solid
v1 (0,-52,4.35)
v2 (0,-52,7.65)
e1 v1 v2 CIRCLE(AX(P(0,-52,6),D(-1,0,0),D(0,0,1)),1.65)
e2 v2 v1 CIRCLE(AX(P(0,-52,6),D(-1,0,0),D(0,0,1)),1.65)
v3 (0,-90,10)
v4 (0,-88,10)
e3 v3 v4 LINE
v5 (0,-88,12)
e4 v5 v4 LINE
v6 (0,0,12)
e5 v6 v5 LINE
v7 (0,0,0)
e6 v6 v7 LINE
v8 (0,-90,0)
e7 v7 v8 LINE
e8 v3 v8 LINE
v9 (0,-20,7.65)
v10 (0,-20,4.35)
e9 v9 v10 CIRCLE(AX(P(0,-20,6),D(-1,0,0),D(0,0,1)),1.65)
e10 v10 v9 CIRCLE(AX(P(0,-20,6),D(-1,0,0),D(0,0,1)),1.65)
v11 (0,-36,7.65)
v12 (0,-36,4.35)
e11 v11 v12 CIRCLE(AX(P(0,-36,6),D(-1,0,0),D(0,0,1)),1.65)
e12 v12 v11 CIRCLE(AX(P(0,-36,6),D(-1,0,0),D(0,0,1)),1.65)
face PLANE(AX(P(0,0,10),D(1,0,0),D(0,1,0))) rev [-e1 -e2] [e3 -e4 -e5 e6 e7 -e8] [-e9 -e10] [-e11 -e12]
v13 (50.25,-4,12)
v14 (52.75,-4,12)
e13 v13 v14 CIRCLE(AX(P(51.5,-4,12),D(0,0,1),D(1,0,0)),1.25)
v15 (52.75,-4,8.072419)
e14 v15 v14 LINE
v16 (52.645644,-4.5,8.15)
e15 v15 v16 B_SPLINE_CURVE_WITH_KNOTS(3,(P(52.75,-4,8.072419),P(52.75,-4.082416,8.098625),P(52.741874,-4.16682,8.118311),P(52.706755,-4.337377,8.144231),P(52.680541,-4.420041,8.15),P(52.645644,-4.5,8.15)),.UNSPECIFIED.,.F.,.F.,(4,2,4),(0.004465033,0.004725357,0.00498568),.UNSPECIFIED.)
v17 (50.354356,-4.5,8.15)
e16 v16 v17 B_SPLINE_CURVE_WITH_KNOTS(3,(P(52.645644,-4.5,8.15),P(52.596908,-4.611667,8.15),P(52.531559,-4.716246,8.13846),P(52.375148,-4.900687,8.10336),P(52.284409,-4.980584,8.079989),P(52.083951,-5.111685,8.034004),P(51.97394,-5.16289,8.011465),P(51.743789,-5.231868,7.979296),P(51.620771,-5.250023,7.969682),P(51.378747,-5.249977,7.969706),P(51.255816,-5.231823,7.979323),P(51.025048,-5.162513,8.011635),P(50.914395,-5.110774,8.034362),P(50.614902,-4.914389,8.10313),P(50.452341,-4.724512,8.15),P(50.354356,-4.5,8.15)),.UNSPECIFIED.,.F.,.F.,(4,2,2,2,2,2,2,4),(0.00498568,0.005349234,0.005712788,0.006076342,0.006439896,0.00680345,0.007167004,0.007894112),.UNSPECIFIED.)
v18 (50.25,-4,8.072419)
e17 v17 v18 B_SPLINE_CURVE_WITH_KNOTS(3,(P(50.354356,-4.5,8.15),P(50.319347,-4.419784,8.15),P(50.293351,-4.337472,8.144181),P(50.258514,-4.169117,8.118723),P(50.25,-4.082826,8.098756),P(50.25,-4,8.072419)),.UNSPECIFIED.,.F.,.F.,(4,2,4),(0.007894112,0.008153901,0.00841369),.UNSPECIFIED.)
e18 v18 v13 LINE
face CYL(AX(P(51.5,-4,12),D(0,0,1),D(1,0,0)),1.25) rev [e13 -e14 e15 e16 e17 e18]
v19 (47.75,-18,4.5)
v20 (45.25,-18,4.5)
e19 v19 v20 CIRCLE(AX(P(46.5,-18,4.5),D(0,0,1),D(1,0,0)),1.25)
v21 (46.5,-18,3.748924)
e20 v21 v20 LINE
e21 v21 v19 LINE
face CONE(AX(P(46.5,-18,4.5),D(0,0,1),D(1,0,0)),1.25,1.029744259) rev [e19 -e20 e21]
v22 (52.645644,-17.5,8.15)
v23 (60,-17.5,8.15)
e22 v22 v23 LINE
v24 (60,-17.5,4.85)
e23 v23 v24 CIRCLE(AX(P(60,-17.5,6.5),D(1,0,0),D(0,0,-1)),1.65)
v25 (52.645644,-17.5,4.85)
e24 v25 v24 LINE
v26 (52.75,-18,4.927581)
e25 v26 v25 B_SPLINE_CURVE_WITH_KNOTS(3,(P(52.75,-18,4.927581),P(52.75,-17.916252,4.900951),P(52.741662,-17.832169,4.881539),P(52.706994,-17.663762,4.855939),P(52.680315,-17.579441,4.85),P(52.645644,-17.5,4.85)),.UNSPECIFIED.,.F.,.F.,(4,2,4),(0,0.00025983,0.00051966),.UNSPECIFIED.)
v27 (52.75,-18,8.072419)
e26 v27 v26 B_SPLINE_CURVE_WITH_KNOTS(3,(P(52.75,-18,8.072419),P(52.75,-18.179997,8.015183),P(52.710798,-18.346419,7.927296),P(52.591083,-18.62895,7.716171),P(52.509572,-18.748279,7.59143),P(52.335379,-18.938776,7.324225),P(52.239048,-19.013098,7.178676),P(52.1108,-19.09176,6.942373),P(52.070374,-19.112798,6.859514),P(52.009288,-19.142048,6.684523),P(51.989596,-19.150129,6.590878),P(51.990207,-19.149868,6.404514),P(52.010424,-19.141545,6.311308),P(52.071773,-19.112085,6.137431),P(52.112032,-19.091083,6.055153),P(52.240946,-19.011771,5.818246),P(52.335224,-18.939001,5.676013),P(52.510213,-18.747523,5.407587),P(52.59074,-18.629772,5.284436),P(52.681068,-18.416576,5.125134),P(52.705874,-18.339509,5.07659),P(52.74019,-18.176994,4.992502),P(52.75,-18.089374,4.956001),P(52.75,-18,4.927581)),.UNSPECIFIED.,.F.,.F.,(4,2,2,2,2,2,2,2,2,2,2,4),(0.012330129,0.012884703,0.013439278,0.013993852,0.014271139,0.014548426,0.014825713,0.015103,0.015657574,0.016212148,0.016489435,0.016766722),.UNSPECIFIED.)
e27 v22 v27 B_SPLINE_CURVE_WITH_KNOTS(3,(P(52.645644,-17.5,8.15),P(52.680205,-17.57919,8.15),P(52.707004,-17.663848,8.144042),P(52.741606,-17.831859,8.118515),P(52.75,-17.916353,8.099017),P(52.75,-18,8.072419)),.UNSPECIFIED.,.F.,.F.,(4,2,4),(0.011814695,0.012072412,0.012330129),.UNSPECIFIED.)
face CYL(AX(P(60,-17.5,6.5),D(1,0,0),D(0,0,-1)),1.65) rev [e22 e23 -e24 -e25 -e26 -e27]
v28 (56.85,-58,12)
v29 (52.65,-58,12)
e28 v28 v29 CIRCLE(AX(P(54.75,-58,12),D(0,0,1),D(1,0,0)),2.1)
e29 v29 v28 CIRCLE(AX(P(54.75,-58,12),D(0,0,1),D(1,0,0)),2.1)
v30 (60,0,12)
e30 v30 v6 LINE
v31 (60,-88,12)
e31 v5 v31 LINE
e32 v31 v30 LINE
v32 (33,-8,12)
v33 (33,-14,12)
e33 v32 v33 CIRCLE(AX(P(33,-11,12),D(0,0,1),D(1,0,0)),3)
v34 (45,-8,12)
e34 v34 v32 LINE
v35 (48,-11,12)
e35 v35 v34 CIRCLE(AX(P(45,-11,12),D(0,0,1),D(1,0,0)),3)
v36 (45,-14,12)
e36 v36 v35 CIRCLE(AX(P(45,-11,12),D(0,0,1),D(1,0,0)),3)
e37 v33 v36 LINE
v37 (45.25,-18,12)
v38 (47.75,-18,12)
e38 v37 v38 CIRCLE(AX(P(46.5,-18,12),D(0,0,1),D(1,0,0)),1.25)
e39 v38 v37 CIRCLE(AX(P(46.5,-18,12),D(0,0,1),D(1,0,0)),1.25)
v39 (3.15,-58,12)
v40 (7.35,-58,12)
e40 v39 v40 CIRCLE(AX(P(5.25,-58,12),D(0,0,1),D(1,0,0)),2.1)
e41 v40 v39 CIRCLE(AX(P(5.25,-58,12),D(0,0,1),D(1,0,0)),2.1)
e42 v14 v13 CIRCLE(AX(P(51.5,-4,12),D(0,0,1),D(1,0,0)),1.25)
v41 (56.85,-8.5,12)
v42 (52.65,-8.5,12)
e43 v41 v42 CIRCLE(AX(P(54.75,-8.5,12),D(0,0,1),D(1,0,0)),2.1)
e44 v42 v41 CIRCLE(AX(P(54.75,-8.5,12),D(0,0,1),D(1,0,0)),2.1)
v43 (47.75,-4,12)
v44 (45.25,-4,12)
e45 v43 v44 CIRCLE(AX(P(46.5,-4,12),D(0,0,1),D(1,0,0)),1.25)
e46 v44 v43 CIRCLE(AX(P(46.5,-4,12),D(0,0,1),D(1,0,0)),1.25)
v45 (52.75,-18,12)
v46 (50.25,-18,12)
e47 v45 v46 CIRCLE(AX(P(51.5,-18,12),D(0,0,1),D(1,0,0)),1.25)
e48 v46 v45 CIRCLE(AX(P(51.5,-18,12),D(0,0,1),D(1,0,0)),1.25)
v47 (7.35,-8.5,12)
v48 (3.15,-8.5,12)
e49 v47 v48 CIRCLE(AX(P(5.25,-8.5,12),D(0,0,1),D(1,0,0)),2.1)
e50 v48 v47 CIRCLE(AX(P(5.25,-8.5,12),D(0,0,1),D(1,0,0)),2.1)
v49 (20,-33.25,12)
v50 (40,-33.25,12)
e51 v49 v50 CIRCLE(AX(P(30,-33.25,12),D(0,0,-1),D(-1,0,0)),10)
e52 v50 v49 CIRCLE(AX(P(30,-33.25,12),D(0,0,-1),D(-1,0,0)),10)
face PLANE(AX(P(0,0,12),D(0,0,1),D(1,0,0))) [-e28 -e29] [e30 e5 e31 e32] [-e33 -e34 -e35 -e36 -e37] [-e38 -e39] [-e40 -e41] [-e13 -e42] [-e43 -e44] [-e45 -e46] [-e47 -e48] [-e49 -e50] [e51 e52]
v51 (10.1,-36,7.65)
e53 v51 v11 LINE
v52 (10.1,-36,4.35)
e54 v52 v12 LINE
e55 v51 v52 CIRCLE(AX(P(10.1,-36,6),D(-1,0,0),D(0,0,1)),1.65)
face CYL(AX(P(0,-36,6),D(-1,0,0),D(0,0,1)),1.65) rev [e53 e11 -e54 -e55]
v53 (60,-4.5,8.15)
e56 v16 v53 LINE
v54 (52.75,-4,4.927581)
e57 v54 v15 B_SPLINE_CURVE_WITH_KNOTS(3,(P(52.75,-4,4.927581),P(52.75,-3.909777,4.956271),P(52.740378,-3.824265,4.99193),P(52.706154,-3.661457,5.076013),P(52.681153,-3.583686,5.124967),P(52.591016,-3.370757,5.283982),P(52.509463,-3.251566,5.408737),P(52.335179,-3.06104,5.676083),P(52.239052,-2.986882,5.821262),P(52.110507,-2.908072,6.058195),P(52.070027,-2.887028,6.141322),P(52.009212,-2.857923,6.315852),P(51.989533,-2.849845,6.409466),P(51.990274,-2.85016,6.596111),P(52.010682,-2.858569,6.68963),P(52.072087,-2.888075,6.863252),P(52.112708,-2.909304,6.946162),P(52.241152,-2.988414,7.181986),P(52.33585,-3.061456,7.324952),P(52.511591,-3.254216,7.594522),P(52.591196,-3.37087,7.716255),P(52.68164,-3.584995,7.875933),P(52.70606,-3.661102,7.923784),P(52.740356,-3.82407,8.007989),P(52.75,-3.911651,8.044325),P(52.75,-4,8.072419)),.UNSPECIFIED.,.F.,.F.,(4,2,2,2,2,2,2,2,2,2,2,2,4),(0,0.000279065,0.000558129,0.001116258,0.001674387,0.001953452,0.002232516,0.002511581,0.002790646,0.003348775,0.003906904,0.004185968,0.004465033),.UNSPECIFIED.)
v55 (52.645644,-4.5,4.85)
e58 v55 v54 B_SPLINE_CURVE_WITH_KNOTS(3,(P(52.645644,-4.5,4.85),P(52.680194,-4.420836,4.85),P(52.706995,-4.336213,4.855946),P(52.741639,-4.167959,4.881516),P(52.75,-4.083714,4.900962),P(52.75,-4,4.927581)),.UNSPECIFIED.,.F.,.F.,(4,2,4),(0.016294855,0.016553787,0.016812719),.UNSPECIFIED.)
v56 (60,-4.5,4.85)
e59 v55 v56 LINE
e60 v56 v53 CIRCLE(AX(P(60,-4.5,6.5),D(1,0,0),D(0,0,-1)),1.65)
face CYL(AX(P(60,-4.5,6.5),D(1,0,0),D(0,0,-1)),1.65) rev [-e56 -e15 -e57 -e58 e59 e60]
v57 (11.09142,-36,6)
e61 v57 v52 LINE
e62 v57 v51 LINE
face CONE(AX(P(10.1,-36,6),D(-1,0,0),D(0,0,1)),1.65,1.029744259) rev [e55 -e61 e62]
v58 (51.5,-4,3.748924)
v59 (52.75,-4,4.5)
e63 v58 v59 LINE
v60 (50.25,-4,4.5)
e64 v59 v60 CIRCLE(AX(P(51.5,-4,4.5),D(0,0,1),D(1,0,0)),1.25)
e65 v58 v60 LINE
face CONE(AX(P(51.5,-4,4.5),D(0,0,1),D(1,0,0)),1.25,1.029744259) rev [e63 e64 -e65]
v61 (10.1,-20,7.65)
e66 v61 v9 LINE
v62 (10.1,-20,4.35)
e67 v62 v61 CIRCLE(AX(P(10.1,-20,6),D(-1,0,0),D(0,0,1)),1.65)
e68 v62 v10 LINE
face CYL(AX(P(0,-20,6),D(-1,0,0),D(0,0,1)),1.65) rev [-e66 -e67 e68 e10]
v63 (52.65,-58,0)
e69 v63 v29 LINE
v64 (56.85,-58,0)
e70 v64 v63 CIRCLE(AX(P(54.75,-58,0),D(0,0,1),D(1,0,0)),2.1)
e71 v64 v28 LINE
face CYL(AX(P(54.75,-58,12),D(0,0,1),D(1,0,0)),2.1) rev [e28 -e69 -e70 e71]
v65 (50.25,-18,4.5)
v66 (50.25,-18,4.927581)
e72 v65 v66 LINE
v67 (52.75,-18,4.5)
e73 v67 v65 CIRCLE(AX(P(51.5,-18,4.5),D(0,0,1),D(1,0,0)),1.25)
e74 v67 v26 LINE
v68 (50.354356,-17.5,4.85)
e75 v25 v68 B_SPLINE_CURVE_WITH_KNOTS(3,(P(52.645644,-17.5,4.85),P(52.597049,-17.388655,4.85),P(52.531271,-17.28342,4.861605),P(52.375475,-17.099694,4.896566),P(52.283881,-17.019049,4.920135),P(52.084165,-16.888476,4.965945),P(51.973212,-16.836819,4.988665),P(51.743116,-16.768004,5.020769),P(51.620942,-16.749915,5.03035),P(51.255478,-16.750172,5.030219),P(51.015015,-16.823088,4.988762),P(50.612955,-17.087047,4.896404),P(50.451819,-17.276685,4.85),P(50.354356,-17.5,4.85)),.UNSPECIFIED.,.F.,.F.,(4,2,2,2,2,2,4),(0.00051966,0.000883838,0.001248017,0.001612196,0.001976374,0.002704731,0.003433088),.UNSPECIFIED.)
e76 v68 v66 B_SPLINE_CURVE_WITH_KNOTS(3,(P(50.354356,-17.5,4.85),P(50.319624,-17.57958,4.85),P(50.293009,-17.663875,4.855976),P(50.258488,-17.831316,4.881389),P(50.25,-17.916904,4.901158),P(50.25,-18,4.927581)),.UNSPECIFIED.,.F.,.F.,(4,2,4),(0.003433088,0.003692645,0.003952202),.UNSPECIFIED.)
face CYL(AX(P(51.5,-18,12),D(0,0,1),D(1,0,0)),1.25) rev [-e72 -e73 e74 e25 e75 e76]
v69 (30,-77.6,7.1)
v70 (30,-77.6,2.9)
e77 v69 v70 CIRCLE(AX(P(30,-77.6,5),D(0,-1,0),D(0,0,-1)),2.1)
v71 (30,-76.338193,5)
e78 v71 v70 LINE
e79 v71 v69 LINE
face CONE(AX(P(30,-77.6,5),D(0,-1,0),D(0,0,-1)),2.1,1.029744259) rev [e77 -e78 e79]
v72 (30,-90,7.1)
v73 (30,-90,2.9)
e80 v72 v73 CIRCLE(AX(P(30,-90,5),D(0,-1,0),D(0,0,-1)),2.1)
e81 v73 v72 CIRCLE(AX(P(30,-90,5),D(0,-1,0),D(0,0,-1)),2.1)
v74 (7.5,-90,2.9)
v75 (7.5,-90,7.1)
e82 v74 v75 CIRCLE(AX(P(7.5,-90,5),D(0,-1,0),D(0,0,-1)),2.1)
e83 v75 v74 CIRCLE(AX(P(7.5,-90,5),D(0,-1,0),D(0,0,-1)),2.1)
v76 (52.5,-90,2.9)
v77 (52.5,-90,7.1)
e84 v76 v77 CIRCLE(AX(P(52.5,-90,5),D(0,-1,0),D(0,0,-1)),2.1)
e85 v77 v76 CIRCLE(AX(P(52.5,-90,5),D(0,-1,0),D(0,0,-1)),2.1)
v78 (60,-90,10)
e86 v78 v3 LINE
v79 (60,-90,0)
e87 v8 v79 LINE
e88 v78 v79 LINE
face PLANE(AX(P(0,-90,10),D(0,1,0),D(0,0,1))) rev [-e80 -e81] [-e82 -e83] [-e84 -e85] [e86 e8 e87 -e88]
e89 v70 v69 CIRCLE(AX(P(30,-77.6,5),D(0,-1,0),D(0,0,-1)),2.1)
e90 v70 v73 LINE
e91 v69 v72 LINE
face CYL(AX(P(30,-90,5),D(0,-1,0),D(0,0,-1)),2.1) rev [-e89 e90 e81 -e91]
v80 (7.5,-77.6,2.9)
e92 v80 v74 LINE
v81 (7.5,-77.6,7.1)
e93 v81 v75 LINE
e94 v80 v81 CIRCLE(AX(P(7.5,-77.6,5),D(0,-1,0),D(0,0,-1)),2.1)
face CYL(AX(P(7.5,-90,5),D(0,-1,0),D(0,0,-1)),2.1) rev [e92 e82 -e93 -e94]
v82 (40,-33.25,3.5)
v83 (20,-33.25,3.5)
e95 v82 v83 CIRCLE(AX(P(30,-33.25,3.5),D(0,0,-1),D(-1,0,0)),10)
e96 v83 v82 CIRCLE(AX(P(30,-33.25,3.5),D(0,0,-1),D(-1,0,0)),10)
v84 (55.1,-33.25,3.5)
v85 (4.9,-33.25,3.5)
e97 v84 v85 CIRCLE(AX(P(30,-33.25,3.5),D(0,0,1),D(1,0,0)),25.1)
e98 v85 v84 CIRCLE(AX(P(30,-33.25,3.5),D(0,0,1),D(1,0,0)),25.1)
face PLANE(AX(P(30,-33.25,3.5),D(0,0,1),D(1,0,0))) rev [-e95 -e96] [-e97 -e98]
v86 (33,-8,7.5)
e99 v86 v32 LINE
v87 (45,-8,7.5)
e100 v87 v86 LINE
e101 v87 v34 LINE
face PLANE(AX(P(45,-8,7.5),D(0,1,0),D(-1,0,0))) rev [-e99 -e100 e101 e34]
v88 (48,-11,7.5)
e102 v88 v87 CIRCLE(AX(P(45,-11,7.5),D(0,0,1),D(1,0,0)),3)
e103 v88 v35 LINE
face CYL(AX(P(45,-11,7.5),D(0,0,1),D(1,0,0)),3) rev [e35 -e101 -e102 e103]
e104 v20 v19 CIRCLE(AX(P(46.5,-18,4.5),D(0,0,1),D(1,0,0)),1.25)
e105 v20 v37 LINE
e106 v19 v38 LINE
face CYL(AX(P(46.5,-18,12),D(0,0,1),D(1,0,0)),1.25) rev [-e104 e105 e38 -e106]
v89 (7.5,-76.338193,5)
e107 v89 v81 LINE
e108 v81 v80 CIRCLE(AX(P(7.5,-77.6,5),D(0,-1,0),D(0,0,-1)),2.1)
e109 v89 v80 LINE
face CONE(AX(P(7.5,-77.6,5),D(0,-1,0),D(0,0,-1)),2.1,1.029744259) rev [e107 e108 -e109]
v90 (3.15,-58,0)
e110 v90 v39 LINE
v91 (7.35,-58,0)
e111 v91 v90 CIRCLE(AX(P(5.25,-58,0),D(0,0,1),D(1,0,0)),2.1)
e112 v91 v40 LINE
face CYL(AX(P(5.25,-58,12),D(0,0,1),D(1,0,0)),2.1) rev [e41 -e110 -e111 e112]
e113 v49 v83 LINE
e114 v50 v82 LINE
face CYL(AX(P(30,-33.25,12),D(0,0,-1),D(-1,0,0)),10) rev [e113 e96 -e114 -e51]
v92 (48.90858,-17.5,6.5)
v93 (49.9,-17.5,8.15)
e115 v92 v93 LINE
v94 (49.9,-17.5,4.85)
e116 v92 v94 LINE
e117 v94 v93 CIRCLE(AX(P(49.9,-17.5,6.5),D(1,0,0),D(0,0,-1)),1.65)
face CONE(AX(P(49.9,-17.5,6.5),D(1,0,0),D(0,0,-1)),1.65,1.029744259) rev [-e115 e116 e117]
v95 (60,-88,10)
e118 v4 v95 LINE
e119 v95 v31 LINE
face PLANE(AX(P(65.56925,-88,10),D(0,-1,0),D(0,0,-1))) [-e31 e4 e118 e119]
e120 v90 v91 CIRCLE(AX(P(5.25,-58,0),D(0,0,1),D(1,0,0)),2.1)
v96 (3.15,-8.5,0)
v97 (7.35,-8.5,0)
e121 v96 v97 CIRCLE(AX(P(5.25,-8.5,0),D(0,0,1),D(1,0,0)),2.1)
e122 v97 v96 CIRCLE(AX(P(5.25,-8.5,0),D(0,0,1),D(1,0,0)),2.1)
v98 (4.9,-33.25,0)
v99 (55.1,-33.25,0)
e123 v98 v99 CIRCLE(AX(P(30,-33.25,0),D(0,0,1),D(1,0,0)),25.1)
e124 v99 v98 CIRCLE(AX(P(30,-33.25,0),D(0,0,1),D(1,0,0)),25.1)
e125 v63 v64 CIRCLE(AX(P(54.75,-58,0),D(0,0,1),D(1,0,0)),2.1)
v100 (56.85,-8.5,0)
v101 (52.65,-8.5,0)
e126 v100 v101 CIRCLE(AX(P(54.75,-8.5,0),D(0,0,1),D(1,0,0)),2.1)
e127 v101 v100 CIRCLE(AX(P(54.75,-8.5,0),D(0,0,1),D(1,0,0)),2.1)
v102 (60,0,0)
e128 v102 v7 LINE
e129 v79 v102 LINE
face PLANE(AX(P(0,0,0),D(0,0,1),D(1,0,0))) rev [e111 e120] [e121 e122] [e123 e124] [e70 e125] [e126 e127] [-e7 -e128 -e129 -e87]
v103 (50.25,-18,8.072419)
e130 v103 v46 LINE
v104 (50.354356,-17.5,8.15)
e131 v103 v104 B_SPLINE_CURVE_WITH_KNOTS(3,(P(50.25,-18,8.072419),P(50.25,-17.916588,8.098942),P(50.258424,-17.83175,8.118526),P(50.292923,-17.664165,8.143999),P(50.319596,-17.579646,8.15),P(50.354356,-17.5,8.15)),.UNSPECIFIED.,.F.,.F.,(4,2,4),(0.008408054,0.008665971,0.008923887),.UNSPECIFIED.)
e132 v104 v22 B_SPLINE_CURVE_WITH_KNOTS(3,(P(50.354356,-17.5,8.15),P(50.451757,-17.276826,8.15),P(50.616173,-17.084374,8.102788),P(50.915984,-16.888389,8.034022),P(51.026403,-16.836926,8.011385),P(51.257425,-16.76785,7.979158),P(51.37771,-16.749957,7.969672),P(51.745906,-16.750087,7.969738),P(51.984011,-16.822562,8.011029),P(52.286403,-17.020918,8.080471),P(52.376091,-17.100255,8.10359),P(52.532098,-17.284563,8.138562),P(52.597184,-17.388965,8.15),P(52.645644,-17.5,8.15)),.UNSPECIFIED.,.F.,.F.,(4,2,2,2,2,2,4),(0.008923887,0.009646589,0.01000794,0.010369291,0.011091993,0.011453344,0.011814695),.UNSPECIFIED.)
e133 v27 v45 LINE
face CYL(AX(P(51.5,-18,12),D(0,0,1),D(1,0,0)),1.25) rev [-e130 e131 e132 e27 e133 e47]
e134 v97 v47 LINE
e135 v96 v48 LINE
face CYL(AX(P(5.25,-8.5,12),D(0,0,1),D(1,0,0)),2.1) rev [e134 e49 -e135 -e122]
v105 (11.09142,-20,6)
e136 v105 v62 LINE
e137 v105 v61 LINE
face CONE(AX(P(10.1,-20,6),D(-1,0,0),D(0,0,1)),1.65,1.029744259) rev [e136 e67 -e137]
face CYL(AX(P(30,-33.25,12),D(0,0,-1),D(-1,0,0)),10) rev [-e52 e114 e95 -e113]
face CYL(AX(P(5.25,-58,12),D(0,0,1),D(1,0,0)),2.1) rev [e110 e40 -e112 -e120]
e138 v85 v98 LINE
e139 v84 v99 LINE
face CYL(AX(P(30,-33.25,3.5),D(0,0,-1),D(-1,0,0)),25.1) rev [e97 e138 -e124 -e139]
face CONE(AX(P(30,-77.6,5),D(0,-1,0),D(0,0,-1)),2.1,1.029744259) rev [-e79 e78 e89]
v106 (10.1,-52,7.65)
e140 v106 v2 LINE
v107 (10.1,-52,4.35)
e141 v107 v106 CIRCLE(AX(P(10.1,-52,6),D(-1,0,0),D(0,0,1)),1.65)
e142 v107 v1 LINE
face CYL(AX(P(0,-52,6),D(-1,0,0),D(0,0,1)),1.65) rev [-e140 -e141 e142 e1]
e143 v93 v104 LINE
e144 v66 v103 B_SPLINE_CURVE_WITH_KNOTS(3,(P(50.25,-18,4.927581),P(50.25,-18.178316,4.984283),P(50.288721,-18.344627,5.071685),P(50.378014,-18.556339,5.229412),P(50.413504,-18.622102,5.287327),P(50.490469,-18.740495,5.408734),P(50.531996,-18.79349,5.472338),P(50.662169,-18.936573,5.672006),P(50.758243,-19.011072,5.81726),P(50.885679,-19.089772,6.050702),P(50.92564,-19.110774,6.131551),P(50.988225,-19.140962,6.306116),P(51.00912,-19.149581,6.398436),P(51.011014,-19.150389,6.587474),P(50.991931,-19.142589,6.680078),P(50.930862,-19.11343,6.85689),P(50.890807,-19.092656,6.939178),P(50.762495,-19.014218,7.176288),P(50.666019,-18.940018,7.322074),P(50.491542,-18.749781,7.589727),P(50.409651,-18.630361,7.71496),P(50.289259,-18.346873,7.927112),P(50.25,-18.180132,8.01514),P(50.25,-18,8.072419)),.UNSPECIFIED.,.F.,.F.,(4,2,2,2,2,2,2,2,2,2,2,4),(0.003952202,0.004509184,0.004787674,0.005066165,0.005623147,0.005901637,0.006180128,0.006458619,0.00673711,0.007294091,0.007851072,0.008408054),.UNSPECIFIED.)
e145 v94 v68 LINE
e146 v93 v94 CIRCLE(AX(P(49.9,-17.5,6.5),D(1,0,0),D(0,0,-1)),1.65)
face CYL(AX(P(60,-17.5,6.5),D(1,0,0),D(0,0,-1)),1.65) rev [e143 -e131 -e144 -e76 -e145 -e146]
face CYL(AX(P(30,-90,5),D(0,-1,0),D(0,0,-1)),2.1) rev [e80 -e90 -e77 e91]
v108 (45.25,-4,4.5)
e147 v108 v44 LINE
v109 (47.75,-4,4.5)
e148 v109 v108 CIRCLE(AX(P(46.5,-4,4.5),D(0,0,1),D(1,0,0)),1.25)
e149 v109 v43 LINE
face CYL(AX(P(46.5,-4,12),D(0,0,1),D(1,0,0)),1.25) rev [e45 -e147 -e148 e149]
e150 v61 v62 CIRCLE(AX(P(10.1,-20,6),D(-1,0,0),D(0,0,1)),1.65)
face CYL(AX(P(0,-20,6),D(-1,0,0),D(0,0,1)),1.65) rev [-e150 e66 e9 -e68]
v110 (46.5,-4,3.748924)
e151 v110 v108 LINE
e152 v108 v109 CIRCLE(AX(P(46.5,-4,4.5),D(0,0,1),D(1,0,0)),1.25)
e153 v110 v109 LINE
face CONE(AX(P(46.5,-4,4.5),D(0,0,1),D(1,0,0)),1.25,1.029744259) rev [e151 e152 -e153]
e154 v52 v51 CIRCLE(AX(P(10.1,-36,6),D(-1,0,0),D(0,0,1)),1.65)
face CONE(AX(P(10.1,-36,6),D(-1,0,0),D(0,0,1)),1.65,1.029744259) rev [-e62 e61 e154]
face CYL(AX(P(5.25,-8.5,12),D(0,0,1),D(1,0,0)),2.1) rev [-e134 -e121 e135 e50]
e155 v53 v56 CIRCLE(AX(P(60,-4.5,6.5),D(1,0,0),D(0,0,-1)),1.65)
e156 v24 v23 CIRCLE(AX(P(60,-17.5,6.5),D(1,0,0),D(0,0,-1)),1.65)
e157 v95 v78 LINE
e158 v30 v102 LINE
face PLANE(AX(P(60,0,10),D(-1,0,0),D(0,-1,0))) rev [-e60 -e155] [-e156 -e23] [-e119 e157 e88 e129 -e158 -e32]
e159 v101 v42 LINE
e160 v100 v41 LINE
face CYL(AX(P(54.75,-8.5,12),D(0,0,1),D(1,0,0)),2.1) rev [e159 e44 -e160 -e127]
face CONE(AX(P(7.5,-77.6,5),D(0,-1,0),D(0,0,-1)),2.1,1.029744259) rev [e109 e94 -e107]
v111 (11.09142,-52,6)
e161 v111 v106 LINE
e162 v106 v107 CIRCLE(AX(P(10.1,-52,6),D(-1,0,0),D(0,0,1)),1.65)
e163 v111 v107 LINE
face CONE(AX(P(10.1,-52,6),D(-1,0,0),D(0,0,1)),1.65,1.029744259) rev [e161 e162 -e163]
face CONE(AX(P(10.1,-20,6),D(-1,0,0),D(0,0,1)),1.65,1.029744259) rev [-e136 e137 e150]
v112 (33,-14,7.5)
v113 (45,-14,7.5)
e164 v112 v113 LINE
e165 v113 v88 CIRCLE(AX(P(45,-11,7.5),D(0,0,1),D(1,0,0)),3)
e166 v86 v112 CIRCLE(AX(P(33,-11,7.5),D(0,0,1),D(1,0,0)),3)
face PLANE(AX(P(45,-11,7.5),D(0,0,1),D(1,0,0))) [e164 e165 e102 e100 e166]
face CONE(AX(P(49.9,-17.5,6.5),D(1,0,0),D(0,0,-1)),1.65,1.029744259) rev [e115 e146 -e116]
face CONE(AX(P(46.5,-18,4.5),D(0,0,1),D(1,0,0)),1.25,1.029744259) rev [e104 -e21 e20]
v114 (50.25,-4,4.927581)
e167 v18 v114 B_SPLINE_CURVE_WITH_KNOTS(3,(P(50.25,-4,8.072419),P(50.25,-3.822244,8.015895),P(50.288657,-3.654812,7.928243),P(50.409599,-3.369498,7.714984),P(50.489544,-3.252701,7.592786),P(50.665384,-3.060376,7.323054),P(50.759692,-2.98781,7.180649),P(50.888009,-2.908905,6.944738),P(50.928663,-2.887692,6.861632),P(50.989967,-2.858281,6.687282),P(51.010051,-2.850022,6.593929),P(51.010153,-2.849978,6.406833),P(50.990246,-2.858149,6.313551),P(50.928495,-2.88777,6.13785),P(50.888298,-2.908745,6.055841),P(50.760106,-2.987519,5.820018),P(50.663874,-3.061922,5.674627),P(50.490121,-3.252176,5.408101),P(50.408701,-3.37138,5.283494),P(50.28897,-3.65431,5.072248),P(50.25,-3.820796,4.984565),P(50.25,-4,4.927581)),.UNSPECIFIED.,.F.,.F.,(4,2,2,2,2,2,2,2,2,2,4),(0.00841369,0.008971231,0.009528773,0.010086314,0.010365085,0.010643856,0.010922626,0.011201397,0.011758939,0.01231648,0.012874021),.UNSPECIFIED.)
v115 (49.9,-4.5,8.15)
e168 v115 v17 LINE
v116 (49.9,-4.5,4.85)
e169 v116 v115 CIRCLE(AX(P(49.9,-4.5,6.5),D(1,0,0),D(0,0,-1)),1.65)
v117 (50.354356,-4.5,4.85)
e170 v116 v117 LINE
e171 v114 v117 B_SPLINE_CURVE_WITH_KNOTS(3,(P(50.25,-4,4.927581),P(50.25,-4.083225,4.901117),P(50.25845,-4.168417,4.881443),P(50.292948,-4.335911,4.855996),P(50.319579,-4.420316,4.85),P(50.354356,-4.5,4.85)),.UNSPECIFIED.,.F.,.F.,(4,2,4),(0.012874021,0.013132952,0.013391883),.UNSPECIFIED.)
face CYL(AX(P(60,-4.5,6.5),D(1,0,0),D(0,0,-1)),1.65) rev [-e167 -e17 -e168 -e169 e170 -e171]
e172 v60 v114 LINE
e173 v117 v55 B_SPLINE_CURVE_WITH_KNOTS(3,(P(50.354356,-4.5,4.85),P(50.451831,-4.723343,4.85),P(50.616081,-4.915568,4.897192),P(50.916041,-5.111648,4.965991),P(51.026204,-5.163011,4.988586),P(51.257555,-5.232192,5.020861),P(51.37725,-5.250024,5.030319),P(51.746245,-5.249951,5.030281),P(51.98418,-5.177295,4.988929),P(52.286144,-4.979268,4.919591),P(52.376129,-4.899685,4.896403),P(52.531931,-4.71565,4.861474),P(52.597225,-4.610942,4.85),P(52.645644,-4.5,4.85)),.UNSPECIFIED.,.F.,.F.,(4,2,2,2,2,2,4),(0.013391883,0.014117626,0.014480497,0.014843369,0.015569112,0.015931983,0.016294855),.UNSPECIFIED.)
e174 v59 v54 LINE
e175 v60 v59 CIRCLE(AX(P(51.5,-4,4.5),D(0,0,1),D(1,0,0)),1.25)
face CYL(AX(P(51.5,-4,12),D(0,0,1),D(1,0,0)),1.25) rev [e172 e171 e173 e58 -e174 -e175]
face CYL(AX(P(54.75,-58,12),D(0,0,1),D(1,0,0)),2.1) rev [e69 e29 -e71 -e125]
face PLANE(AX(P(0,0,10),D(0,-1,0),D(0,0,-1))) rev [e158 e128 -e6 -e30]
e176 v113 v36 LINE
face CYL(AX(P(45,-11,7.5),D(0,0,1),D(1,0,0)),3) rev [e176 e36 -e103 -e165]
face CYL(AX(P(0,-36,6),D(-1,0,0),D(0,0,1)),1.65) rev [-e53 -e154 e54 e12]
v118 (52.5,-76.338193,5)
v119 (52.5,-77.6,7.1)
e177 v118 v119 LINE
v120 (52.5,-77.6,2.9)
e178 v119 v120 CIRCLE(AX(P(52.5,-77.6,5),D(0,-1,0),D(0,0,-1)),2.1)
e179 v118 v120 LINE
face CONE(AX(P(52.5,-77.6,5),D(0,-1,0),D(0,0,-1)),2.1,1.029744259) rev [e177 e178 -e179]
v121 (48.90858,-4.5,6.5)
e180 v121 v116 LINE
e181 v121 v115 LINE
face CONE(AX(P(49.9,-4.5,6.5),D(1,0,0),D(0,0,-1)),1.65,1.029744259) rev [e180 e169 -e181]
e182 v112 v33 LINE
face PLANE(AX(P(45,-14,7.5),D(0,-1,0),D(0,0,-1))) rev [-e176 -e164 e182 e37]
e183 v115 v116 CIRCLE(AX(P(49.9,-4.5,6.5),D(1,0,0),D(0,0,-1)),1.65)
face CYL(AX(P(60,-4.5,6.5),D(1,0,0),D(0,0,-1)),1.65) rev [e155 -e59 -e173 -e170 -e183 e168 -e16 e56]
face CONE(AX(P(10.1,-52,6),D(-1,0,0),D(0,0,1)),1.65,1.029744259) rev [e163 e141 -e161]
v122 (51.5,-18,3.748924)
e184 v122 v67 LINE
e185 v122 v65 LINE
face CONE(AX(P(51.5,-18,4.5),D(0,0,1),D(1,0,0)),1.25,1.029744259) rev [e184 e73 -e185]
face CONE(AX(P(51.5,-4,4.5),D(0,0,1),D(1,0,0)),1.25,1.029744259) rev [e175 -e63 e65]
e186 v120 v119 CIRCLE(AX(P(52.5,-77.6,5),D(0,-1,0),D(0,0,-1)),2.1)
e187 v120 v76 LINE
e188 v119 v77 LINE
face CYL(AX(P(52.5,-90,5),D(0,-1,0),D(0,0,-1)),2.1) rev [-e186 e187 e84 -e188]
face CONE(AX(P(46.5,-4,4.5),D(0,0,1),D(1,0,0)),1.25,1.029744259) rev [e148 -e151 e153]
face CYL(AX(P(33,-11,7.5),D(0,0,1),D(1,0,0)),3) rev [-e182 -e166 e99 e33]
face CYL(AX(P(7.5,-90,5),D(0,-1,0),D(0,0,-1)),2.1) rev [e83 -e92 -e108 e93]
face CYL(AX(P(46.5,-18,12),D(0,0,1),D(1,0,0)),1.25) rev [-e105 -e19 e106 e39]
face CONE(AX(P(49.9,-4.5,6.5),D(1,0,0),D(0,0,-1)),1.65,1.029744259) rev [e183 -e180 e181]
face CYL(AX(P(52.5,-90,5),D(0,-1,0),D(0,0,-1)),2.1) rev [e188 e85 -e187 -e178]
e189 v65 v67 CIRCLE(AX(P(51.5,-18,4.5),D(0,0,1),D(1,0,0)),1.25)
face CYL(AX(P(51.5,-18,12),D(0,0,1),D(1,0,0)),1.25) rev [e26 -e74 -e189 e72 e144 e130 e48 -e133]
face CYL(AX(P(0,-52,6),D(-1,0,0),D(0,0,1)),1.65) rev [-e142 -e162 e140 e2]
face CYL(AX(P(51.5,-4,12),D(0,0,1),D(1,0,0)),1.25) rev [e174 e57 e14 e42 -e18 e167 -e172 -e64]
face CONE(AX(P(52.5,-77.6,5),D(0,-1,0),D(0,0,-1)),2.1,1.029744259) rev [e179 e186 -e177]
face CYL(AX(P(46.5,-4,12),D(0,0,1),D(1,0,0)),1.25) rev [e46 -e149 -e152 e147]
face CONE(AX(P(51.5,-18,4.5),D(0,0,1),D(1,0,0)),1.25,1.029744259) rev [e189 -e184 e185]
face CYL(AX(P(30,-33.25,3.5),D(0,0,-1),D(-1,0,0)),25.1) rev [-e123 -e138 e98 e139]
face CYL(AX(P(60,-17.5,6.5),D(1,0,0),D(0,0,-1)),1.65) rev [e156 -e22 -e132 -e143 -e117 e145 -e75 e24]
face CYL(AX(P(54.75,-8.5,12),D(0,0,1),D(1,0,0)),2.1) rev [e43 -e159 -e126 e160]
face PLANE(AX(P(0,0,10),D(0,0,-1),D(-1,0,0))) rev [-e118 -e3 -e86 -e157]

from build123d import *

# Parameters (mm, degrees)
SKETCH1_W             = 60
SKETCH1_H             = 90
BOSS_EXTRUDE1_DEPTH   = 10
M5_TAPPED_HOLE1_D     = 4.2
M5_TAPPED_HOLE1_DEPTH = 12.4
M5_TAPPED_HOLE1_TIP   = 1.2618073
MOVE_FACE1_BY         = 2
SKETCH13_W            = 86.920881712
SKETCH13_H            = 2
CUT_EXTRUDE5_DEPTH    = 2
M5_TAPPED_HOLE2_D     = 4.2
SKETCH16_R            = 25.1
CUT_EXTRUDE6_DEPTH    = 3.5
M4_TAPPED_HOLE2_D     = 3.3
M4_TAPPED_HOLE2_DEPTH = 10.1
M4_TAPPED_HOLE2_TIP   = 0.991420021
SKETCH19_R            = 10
CUT_EXTRUDE7_DEPTH    = 109.5
M3_TAPPED_HOLE2_D     = 2.5
M3_TAPPED_HOLE2_DEPTH = 7.5
M3_TAPPED_HOLE2_TIP   = 0.751075774
M4_TAPPED_HOLE3_D     = 3.3
M4_TAPPED_HOLE3_DEPTH = 10.1
M4_TAPPED_HOLE3_TIP   = 0.991420021
CUT_EXTRUDE8_DEPTH    = 4.5


with BuildPart() as part:
    # Sketch1 → Boss-Extrude1 (new body)
    with BuildSketch(Plane.XY):
        with Locations((30, -45)):
            Rectangle(SKETCH1_W, SKETCH1_H)
    extrude(amount=BOSS_EXTRUDE1_DEPTH)

    # M5 Tapped Hole1
    with Locations(Plane(origin=(0, -90, 0), x_dir=(-1, 0, 0), z_dir=(0, -1, 0))):
        with Locations((-7.5, -5), (-52.5, -5), (-30, -5)):
            Hole(M5_TAPPED_HOLE1_D / 2, depth=M5_TAPPED_HOLE1_DEPTH)
            with Locations((0, 0, -(M5_TAPPED_HOLE1_DEPTH + M5_TAPPED_HOLE1_TIP / 2))):  # 118° drill point
                Cone(0, M5_TAPPED_HOLE1_D / 2, M5_TAPPED_HOLE1_TIP, mode=Mode.SUBTRACT)

    # Move Face1: a face moved outward by 2.0
    extrude(part.faces().sort_by_distance((30, -45, 10))[0], amount=MOVE_FACE1_BY, dir=(0, 0, 1))

    # Sketch13 → Cut-Extrude5 (cut)
    with BuildSketch(Plane(origin=(0, 0, 12), x_dir=(-1, 0, 0), z_dir=(0, 0, -1))):
        with Locations((-22.108808842, -89)):
            Rectangle(SKETCH13_W, SKETCH13_H)
    extrude(amount=CUT_EXTRUDE5_DEPTH, mode=Mode.SUBTRACT)

    # M5 Tapped Hole2 (through all)
    with Locations(Plane.XY.offset(12)):
        with Locations((5.25, -8.5), (54.75, -8.5), (54.75, -58), (5.25, -58)):
            Hole(M5_TAPPED_HOLE2_D / 2)

    # Sketch16 → Cut-Extrude6 (cut)
    with BuildSketch(Plane.XY):
        with Locations((30, -33.25)):
            Circle(SKETCH16_R)
    extrude(amount=CUT_EXTRUDE6_DEPTH, mode=Mode.SUBTRACT)

    # M4 Tapped Hole2
    with Locations(Plane.ZY):
        with Locations((6, -20), (6, -36), (6, -52)):
            Hole(M4_TAPPED_HOLE2_D / 2, depth=M4_TAPPED_HOLE2_DEPTH)
            with Locations((0, 0, -(M4_TAPPED_HOLE2_DEPTH + M4_TAPPED_HOLE2_TIP / 2))):  # 118° drill point
                Cone(0, M4_TAPPED_HOLE2_D / 2, M4_TAPPED_HOLE2_TIP, mode=Mode.SUBTRACT)

    # Sketch19 → Cut-Extrude7 (cut, through all)
    with BuildSketch(Plane(origin=(0, 0, 3.5), x_dir=(-1, 0, 0), z_dir=(0, 0, -1))):
        with Locations((-30, -33.25)):
            Circle(SKETCH19_R)
    extrude(amount=-CUT_EXTRUDE7_DEPTH, mode=Mode.SUBTRACT)

    # M3 Tapped Hole2
    with Locations(Plane.XY.offset(12)):
        with Locations((51.5, -18), (51.5, -4), (46.5, -18), (46.5, -4)):
            Hole(M3_TAPPED_HOLE2_D / 2, depth=M3_TAPPED_HOLE2_DEPTH)
            with Locations((0, 0, -(M3_TAPPED_HOLE2_DEPTH + M3_TAPPED_HOLE2_TIP / 2))):  # 118° drill point
                Cone(0, M3_TAPPED_HOLE2_D / 2, M3_TAPPED_HOLE2_TIP, mode=Mode.SUBTRACT)

    # M4 Tapped Hole3
    with Locations(Plane(origin=(60, 0, 0), x_dir=(0, 0, -1), z_dir=(1, 0, 0))):
        with Locations((-6.5, -4.5), (-6.5, -17.5)):
            Hole(M4_TAPPED_HOLE3_D / 2, depth=M4_TAPPED_HOLE3_DEPTH)
            with Locations((0, 0, -(M4_TAPPED_HOLE3_DEPTH + M4_TAPPED_HOLE3_TIP / 2))):  # 118° drill point
                Cone(0, M4_TAPPED_HOLE3_D / 2, M4_TAPPED_HOLE3_TIP, mode=Mode.SUBTRACT)

    # Sketch25 → Cut-Extrude8 (cut)
    with BuildSketch(Plane.XY.offset(12)):
        with BuildLine():
            Line((45, -14), (33, -14))
            ThreePointArc((33, -14), (30, -11), (33, -8))
            Line((33, -8), (45, -8))
            ThreePointArc((45, -8), (48, -11), (45, -14))
        make_face()
    extrude(amount=-CUT_EXTRUDE8_DEPTH, mode=Mode.SUBTRACT)


solid = part.part
